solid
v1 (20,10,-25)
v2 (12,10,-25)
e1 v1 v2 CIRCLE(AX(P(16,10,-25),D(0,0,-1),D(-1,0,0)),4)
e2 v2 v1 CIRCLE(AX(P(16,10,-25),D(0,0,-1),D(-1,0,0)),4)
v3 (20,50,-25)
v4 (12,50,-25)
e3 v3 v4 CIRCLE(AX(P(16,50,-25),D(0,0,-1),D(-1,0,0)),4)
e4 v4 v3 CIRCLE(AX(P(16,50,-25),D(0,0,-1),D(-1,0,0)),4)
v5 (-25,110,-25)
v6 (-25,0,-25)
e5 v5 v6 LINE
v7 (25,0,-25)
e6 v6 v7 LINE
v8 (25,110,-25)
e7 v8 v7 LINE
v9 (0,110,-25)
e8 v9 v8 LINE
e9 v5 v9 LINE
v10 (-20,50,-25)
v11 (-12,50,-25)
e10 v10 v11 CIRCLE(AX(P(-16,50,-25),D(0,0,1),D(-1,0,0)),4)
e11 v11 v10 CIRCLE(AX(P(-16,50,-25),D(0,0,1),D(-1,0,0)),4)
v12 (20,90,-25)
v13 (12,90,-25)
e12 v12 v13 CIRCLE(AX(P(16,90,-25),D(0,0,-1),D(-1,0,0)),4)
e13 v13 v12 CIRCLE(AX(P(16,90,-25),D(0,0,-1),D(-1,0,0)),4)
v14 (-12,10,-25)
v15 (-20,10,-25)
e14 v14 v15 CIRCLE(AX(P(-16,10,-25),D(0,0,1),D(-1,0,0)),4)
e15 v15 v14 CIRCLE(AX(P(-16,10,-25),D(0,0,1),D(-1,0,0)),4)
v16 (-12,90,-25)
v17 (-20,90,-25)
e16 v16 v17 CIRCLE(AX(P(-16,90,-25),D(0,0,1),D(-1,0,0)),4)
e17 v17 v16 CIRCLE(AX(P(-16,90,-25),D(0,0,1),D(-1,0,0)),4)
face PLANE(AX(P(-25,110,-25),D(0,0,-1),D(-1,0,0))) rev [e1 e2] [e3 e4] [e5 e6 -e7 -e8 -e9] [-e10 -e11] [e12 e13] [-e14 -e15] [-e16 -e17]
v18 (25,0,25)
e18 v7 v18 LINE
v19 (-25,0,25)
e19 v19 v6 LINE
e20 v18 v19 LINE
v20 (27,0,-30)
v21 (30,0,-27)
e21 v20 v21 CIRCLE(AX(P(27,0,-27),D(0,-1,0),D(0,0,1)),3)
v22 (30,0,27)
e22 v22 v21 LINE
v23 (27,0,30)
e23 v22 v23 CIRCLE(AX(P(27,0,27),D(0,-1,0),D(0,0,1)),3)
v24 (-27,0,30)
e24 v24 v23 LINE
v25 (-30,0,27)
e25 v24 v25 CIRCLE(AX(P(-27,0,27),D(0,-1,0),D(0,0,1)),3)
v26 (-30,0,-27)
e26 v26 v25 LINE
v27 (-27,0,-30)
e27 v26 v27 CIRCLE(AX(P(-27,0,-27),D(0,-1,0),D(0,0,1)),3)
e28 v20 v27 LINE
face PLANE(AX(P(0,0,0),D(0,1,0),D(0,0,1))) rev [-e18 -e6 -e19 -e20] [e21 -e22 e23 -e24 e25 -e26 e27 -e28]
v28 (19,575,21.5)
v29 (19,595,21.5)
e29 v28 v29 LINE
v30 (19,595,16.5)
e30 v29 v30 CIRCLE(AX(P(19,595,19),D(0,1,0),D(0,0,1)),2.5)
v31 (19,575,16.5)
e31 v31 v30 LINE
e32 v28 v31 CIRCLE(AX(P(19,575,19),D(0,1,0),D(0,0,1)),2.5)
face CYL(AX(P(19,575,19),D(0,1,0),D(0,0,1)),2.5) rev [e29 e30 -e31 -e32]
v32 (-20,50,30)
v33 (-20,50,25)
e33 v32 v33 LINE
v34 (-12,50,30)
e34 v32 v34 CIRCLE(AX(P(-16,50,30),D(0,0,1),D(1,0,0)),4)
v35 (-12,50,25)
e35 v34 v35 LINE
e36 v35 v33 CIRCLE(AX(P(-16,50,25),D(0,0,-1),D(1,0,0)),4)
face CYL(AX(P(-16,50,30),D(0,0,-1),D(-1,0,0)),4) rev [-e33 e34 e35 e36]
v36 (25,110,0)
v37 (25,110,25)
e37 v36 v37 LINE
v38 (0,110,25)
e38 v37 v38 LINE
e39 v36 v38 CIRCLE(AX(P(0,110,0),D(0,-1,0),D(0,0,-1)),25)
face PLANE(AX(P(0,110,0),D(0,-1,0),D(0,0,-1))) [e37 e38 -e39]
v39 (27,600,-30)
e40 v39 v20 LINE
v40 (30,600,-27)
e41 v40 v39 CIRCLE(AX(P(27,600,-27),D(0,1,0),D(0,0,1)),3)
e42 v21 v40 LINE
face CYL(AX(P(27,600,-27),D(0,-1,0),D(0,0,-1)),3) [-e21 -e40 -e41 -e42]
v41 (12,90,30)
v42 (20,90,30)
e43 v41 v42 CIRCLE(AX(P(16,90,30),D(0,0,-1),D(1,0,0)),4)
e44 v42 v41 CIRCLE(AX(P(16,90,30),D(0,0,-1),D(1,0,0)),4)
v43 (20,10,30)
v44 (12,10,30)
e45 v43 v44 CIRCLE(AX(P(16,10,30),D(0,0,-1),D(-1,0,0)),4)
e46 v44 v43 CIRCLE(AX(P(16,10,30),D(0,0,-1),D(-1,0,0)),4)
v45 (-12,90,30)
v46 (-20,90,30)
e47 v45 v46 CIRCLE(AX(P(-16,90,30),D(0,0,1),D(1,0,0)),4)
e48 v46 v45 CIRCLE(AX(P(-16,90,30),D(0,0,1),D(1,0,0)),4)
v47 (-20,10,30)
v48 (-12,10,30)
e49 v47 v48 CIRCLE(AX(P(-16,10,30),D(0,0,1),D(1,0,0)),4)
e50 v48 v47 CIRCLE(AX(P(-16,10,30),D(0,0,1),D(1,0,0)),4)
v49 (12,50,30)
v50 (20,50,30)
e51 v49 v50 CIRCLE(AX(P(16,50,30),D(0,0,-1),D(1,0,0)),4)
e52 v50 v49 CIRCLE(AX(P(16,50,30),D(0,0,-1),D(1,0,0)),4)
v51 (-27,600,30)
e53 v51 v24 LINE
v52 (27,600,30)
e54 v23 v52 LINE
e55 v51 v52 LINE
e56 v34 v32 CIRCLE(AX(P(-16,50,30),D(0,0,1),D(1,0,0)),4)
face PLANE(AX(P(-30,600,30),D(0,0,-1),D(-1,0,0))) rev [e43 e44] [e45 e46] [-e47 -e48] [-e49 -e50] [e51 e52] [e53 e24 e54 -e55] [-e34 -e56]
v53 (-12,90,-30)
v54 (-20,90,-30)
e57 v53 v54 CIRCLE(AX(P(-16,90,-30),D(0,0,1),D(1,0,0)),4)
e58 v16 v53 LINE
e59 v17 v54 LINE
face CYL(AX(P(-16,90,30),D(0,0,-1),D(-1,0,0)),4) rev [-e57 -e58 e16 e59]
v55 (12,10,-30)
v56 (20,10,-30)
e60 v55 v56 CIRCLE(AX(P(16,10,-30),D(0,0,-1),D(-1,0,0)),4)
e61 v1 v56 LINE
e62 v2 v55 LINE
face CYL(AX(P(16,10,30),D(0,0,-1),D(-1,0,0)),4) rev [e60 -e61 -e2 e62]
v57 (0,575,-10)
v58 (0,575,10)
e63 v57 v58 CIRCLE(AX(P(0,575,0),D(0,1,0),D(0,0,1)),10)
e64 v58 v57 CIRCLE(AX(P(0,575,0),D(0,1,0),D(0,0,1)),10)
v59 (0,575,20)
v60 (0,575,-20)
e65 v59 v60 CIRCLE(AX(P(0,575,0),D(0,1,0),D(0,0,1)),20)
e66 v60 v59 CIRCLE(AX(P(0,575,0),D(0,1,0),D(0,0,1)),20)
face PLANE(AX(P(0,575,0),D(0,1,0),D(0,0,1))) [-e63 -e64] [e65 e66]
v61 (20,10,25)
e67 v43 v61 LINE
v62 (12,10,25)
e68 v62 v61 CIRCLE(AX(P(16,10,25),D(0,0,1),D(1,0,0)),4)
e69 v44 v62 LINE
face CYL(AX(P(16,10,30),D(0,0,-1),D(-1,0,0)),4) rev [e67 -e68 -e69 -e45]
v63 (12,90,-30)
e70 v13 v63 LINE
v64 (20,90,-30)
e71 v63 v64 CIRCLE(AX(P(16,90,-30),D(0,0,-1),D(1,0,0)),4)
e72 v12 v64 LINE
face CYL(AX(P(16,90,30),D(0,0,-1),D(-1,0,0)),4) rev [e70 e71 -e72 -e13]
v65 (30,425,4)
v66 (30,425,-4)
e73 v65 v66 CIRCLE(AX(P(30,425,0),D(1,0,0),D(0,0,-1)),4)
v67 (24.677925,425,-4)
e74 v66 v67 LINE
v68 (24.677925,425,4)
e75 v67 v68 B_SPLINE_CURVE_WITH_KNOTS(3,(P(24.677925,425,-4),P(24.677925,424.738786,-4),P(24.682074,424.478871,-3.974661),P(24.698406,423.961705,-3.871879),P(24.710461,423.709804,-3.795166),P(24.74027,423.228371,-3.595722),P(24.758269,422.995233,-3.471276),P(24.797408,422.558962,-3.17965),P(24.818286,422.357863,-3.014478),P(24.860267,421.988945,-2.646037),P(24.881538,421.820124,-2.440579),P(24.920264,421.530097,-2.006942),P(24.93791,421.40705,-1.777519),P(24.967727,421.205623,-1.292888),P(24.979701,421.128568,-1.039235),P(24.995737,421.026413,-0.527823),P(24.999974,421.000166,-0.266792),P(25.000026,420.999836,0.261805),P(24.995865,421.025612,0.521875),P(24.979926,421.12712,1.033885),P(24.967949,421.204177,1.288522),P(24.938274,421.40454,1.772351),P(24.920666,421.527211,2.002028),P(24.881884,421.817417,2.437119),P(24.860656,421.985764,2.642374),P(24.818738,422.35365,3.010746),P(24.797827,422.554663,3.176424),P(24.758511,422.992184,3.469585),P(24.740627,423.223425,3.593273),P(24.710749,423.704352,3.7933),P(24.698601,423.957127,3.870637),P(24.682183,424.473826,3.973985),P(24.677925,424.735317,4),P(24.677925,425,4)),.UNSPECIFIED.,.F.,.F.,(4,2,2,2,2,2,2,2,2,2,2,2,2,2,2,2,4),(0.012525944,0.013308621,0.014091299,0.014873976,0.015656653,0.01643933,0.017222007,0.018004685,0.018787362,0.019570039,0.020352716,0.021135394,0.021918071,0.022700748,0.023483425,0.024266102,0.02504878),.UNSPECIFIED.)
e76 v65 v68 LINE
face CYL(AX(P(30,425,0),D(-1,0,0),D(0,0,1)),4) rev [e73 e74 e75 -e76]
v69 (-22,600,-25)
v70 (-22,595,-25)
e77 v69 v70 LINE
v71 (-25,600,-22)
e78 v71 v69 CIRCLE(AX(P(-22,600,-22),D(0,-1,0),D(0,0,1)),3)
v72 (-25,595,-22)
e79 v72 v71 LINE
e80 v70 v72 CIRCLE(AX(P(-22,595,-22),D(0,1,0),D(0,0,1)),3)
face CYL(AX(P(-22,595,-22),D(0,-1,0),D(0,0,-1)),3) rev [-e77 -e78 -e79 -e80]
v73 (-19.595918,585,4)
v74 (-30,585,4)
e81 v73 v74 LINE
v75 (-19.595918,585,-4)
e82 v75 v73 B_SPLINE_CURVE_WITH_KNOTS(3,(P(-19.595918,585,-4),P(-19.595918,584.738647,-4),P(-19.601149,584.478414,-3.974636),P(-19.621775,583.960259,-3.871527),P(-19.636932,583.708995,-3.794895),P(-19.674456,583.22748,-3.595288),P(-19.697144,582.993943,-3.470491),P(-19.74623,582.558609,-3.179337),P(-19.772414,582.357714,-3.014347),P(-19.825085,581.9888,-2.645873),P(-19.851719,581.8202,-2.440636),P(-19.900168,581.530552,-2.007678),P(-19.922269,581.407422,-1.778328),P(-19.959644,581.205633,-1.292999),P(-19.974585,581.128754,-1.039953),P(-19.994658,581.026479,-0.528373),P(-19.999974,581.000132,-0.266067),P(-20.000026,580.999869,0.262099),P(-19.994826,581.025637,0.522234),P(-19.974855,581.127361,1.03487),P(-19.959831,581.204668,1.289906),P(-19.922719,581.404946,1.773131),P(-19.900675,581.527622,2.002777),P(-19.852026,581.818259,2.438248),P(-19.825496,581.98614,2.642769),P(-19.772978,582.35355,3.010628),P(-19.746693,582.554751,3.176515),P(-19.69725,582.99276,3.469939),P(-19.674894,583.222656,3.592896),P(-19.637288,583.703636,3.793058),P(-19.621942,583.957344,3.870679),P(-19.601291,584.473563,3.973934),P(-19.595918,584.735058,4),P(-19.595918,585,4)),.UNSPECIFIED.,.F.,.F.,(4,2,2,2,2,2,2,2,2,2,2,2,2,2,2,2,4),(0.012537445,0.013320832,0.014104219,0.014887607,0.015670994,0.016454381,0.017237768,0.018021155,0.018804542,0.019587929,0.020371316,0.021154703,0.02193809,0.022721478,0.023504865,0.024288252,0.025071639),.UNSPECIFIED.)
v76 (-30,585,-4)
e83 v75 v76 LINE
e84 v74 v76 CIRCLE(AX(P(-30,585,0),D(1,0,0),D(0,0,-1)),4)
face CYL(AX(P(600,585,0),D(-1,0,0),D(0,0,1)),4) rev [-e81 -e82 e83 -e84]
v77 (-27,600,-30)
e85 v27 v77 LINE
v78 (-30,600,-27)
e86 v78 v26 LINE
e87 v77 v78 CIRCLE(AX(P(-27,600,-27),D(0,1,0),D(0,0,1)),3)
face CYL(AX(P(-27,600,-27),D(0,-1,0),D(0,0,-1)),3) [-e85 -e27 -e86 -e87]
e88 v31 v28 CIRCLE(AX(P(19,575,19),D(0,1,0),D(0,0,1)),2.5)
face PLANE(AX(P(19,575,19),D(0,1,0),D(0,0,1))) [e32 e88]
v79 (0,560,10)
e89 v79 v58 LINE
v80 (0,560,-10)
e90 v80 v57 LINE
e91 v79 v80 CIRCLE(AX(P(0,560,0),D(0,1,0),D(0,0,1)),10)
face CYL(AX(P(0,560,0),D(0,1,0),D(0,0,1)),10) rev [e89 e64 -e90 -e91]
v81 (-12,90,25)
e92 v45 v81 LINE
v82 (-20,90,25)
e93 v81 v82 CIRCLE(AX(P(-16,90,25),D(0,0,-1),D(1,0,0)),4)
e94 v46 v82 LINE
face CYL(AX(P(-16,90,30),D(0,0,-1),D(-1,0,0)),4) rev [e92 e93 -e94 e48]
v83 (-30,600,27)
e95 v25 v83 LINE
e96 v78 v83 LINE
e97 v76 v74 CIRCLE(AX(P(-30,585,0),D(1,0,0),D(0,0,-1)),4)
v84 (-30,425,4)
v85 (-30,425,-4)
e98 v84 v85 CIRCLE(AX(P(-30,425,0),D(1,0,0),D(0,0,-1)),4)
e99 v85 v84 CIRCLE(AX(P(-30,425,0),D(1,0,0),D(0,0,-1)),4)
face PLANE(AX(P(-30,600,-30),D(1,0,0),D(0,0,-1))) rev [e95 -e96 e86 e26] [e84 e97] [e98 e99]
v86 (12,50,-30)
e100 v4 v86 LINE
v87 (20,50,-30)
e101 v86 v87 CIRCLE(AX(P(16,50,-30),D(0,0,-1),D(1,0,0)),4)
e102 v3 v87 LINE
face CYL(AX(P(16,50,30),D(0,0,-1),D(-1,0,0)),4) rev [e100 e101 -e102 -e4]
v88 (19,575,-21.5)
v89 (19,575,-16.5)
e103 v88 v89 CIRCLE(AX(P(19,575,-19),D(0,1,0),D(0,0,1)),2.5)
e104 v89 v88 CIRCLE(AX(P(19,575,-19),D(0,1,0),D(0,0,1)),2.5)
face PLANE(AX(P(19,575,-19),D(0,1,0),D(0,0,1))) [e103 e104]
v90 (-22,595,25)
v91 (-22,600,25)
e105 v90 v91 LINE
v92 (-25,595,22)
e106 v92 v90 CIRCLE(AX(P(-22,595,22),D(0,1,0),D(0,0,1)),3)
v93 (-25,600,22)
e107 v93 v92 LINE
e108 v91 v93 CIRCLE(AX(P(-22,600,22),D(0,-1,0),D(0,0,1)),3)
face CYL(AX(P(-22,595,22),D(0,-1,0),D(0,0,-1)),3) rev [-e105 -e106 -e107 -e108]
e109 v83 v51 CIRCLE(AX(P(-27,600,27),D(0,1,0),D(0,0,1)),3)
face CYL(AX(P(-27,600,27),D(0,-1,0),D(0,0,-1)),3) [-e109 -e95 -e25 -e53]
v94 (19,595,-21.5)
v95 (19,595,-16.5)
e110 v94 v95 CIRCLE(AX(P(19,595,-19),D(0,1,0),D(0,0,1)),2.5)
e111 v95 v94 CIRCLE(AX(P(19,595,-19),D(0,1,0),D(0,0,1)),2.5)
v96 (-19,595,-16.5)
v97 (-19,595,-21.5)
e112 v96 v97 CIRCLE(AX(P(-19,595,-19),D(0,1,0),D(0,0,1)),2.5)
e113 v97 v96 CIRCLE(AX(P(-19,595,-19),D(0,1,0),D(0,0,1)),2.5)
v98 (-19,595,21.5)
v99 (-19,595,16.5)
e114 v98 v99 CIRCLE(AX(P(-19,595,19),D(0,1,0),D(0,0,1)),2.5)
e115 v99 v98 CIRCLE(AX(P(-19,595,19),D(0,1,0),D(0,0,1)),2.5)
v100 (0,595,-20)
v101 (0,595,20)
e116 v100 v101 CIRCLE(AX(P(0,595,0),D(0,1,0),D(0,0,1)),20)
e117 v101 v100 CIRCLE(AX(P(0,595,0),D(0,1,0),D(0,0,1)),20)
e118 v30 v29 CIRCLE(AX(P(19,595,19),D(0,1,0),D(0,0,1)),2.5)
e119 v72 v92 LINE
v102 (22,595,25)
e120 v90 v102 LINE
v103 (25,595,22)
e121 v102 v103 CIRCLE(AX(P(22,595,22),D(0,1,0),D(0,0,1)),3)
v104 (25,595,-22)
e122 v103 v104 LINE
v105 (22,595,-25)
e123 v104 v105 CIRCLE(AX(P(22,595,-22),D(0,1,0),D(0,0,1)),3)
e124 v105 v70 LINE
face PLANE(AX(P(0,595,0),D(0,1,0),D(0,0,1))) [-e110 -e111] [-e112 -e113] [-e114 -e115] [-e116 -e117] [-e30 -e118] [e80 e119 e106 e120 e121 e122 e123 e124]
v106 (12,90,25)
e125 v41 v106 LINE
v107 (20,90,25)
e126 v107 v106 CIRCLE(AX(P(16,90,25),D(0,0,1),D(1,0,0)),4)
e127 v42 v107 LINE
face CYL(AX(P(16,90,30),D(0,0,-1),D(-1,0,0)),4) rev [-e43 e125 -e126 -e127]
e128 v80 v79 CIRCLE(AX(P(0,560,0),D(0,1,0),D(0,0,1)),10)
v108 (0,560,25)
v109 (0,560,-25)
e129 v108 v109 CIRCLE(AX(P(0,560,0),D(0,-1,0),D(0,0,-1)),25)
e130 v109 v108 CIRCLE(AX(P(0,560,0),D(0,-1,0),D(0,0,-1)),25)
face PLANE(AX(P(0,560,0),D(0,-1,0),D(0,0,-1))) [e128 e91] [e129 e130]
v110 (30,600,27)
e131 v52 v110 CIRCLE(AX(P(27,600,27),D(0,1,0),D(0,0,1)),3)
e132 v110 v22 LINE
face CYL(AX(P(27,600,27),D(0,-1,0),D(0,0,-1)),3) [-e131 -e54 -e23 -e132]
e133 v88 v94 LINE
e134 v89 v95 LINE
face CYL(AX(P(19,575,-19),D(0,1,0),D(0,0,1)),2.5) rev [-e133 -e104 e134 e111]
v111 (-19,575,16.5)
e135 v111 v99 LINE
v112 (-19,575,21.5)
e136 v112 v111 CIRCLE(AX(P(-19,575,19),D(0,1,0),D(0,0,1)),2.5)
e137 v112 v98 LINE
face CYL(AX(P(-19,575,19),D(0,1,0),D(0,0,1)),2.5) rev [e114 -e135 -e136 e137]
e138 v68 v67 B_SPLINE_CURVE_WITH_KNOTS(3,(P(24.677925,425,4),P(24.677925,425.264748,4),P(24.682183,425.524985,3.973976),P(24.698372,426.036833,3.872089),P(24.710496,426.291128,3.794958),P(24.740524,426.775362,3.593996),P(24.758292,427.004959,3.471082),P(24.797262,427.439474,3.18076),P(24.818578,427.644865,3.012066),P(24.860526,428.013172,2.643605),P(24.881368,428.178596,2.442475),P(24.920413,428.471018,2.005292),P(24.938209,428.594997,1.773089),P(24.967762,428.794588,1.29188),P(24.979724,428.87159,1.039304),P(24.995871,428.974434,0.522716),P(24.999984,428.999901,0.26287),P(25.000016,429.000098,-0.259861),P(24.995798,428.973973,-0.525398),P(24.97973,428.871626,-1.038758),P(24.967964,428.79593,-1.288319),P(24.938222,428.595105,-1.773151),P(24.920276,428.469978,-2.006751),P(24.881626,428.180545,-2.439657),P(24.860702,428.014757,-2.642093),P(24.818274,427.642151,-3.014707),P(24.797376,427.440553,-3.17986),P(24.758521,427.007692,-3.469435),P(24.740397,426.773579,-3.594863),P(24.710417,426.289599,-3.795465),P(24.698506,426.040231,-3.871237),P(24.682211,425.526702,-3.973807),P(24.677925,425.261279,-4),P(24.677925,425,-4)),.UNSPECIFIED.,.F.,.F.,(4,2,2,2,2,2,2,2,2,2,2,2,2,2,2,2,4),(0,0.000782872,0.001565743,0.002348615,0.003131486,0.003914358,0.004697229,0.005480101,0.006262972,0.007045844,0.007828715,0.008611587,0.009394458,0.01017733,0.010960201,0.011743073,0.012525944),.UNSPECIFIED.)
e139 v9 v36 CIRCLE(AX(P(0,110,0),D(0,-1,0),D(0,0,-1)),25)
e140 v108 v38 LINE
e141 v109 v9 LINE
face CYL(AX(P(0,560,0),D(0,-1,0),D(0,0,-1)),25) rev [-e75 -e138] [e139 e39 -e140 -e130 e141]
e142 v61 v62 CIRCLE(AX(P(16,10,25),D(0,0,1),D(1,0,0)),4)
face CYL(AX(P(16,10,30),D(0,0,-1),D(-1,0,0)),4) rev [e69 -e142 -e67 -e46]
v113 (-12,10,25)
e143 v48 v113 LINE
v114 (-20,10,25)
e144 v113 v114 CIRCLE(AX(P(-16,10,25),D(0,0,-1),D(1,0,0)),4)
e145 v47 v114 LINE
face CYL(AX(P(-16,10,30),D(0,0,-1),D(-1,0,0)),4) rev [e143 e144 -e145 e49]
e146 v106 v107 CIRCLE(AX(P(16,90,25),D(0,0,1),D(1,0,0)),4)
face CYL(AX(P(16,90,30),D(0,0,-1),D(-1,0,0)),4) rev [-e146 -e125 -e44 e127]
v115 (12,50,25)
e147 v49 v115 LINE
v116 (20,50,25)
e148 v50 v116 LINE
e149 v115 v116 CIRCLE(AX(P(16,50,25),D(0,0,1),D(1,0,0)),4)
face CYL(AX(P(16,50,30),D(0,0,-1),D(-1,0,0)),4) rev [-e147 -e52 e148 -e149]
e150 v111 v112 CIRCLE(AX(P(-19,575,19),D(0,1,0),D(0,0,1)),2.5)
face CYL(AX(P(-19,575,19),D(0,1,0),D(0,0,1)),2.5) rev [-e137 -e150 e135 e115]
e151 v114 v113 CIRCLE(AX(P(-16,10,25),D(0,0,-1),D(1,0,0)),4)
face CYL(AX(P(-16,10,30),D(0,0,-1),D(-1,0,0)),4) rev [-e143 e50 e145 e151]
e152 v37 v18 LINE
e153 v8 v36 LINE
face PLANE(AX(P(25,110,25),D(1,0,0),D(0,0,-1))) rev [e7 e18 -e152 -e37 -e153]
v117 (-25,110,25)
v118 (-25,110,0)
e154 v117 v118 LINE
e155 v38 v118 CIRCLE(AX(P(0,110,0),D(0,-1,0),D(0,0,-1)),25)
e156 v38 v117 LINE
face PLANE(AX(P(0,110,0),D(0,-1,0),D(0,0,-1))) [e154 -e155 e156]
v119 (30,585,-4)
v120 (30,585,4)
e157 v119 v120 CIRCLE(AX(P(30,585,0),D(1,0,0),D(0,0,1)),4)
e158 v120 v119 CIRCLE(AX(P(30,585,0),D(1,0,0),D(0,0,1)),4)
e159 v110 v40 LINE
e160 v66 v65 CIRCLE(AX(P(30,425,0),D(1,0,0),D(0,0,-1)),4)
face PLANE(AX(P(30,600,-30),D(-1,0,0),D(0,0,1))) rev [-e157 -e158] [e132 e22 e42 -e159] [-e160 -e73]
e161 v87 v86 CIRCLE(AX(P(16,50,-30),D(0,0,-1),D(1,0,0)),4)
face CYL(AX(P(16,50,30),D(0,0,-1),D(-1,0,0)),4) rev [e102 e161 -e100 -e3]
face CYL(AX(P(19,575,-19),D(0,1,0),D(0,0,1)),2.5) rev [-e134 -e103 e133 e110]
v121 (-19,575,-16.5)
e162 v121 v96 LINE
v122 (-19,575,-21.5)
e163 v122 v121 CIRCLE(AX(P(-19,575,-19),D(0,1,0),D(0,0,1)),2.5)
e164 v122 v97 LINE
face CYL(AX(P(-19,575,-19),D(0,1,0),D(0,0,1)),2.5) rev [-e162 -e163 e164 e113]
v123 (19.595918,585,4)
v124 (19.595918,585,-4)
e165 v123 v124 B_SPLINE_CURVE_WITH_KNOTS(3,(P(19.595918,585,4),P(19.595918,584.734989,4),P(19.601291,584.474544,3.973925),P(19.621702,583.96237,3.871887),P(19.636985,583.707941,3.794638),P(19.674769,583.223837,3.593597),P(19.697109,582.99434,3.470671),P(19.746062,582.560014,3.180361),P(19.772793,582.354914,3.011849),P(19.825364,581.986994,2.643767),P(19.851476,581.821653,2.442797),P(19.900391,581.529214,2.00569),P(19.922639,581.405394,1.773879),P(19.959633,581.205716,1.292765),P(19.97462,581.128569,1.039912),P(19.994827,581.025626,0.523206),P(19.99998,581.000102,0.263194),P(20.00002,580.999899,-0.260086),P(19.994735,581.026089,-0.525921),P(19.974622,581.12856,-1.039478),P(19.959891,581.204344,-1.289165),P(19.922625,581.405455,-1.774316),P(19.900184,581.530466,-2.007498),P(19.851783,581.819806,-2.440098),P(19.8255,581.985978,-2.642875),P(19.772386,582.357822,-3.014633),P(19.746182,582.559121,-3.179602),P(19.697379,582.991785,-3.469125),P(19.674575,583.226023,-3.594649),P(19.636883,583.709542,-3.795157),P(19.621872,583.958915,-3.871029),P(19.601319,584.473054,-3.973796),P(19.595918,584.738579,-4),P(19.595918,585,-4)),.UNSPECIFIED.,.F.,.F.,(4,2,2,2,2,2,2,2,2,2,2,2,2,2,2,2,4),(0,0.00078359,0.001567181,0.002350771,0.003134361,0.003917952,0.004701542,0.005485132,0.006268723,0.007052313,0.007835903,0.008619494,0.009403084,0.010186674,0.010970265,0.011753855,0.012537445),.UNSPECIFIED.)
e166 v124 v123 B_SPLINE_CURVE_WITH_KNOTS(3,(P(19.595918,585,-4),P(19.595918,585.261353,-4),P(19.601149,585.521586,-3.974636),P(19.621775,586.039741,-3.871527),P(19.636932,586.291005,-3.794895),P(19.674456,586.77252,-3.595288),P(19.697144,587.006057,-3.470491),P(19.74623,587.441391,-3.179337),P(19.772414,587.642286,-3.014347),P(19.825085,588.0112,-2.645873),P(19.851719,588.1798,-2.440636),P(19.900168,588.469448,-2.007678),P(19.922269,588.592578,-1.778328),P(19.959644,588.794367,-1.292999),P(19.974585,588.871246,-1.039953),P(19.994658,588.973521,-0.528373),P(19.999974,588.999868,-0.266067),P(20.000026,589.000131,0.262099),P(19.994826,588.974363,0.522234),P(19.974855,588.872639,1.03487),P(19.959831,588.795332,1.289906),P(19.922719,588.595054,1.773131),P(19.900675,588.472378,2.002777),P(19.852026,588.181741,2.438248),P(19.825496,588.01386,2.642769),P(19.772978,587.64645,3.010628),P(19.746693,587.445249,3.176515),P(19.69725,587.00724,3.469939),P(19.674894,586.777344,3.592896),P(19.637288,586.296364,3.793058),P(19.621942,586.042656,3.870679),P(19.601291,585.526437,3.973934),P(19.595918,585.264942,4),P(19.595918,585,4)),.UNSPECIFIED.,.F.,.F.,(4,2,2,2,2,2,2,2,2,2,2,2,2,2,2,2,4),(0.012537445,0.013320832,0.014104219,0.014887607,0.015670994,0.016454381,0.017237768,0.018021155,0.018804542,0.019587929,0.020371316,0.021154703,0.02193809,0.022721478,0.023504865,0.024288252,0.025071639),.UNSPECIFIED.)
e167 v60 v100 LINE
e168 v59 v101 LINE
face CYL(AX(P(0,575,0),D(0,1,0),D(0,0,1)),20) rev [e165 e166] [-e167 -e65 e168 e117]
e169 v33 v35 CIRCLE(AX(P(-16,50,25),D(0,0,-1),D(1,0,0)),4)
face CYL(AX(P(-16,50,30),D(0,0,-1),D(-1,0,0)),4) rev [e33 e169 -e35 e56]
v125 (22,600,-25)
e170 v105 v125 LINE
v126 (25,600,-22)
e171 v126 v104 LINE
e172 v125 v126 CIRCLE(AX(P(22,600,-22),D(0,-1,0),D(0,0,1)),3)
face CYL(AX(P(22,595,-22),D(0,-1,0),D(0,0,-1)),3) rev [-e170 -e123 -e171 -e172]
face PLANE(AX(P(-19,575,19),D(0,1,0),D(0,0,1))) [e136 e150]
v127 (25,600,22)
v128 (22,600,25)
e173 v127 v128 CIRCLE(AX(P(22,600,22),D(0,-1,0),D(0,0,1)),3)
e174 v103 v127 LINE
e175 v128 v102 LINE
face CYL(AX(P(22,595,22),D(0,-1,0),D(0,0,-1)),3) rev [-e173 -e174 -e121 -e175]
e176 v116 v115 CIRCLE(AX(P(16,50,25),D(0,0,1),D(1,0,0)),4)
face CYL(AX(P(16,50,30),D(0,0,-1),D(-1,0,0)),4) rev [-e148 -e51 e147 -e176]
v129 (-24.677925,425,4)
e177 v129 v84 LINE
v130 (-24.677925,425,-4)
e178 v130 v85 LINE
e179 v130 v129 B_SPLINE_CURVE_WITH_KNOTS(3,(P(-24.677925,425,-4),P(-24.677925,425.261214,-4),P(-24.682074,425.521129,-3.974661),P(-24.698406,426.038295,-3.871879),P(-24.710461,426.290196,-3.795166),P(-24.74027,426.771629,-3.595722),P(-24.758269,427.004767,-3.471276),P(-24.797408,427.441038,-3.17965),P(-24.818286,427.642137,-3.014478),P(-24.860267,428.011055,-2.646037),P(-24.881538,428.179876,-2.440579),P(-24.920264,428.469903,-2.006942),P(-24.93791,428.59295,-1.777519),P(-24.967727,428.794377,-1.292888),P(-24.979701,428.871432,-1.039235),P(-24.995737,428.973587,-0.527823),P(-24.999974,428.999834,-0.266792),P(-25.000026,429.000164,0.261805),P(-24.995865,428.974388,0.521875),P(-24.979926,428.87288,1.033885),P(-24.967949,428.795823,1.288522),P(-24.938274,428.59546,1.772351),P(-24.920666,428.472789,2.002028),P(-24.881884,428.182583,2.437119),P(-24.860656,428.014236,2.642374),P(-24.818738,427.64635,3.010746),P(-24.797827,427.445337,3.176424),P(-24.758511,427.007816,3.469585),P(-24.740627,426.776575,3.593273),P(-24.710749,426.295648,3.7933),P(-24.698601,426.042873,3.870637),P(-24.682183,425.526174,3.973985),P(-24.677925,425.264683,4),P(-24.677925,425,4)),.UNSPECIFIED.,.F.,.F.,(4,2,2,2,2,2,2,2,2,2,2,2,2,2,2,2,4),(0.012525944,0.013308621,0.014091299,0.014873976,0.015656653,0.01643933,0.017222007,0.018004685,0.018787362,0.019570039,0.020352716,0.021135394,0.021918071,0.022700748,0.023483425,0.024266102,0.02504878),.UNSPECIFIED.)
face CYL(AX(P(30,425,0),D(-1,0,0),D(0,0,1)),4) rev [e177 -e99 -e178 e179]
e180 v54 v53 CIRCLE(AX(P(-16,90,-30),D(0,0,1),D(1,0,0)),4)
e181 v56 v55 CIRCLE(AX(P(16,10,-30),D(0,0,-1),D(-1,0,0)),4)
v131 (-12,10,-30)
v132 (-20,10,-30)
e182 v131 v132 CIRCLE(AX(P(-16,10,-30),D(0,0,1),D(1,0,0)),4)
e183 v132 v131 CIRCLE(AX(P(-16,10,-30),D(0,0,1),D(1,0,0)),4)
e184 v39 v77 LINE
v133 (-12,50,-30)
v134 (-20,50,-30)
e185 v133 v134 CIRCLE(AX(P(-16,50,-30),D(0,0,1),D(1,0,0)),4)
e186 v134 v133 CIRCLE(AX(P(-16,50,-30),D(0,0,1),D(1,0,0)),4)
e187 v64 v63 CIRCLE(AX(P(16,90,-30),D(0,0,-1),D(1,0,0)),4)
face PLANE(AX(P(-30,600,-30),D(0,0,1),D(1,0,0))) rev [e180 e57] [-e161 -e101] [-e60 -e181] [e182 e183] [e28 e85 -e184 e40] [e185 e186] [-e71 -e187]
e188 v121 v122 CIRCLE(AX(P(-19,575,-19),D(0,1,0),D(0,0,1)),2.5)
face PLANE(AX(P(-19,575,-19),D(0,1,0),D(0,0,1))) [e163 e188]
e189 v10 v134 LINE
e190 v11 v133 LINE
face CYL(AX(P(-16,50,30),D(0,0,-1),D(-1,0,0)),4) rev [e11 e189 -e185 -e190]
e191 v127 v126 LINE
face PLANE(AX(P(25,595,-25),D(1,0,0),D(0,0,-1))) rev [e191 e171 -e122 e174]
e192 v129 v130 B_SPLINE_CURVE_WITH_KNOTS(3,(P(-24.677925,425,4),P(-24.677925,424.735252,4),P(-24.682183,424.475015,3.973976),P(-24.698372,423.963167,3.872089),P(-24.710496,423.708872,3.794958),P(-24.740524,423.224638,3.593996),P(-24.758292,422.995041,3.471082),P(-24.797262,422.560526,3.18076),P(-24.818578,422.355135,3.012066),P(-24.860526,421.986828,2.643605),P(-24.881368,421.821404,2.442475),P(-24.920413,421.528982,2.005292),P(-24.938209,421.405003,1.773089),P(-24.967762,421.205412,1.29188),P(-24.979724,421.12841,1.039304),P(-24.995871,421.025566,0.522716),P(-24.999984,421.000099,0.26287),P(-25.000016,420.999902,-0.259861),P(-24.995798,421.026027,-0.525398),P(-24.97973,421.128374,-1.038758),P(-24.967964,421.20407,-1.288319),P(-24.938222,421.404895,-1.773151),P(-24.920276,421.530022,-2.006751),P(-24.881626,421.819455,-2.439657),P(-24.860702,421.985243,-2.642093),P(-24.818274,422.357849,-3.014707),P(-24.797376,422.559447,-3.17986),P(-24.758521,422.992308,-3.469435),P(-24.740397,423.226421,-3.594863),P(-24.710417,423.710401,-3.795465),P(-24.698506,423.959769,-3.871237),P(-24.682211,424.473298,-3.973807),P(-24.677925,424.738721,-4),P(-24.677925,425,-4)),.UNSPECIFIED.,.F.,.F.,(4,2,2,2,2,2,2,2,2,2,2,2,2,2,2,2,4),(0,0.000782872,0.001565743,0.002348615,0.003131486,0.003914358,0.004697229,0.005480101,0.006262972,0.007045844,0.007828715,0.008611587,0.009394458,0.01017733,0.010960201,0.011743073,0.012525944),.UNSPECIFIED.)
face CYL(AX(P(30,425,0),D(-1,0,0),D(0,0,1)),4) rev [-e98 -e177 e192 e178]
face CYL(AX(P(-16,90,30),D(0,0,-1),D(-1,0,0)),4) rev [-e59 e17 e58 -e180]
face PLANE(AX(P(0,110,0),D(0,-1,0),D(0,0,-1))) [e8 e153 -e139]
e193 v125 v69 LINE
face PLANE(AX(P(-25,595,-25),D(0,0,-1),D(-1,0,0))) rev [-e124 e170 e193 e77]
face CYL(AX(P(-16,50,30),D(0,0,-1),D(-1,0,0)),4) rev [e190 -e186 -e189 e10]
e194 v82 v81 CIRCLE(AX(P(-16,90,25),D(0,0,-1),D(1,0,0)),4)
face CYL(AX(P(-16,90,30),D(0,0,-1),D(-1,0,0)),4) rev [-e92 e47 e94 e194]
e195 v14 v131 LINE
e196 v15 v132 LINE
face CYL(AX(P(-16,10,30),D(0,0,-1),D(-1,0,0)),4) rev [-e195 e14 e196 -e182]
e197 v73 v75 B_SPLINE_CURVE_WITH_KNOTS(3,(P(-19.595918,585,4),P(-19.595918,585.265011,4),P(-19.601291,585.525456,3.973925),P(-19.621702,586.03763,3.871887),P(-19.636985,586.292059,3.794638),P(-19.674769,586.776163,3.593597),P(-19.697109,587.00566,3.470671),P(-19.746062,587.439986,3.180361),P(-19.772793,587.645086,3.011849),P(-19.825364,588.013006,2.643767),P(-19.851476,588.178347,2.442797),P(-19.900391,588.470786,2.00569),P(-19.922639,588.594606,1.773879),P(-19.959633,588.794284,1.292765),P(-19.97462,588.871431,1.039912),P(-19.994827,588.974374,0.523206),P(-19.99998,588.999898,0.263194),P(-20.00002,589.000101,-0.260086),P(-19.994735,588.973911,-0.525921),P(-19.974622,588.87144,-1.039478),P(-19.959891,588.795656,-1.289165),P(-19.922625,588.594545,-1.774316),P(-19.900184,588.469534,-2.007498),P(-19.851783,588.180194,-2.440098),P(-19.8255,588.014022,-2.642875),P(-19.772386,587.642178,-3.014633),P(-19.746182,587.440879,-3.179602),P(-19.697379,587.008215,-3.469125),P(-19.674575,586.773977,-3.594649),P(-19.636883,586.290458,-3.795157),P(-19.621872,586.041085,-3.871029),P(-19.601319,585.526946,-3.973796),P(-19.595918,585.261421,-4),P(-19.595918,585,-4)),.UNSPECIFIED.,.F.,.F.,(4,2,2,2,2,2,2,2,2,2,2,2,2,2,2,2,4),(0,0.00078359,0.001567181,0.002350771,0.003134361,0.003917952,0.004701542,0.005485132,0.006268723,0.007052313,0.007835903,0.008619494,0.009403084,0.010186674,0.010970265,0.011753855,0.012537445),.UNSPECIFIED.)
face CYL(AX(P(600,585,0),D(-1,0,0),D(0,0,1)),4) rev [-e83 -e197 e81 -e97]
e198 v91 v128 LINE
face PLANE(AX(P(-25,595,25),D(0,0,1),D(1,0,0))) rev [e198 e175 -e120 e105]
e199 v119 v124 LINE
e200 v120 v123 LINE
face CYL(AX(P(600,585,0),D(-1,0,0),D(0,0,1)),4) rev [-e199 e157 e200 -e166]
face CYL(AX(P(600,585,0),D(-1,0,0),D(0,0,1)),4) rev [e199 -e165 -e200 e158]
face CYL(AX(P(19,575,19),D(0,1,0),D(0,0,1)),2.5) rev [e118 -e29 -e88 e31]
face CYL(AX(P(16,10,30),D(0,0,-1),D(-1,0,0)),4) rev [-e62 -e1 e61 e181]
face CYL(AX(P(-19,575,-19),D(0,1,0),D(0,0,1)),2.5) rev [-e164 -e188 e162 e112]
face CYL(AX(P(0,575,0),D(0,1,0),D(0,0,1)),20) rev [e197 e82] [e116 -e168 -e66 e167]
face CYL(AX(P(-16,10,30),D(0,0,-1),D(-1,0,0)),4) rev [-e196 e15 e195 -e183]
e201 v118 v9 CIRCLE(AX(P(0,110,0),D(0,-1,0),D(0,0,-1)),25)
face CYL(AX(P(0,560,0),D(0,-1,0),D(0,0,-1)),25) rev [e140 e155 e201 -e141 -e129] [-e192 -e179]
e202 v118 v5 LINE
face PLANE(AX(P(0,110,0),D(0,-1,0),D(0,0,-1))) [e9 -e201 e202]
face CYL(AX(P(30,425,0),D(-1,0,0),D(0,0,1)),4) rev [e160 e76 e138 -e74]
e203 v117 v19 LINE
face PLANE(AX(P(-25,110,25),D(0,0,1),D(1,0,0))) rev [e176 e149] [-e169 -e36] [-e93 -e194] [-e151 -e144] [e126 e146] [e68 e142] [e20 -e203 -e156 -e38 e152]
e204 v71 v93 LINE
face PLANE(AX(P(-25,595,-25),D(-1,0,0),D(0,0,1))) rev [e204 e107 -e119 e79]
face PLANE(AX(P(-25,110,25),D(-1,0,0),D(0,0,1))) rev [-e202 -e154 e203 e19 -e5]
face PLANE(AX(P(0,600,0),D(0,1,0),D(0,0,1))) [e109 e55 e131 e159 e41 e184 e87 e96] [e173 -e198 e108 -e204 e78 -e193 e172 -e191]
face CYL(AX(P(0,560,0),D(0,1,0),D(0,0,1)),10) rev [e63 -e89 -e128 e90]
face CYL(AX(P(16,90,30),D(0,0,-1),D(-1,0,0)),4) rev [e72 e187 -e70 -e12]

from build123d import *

# Parameters (mm, degrees)
SKETCH1_W               = 60
SKETCH1_H               = 60
BOSS_EXTRUDE1_DEPTH     = 600
SKETCH2_W               = 50
SKETCH2_H               = 50
CUT_EXTRUDE1_DEPTH      = 5
CUT_EXTRUDE3_DEPTH      = 600
CUT_EXTRUDE3_DEPTH_BACK = 30
SKETCH4_R               = 4
FILLET2_R               = 3
SKETCH3_R               = 20
CUT_EXTRUDE4_DEPTH      = 20
SKETCH5_W               = 50
SKETCH5_H               = 50
CUT_EXTRUDE5_DEPTH      = 110
SKETCH6_R               = 25
CUT_EXTRUDE6_DEPTH      = 450
SKETCH7_R               = 10
CUT_EXTRUDE7_DEPTH      = 15
FILLET4_R               = 3
CUT_EXTRUDE8_DEPTH      = 30
CUT_EXTRUDE8_DEPTH_BACK = 30
SKETCH8_R               = 4
CUT_EXTRUDE9_DEPTH      = 30
CUT_EXTRUDE9_DEPTH_BACK = 30
SKETCH9_R               = 4
SKETCH10_R              = 2.5
CUT_EXTRUDE10_DEPTH     = 20


with BuildPart() as part:
    # Sketch1 → Boss-Extrude1 (new body)
    with BuildSketch(Plane(origin=(0, 0, 0), x_dir=(1, 0, 0), z_dir=(0, 1, 0))):
        Rectangle(SKETCH1_W, SKETCH1_H)
    extrude(amount=BOSS_EXTRUDE1_DEPTH)

    # Sketch2 → Cut-Extrude1 (cut)
    with BuildSketch(Plane(origin=(0, 600, 0), x_dir=(1, 0, 0), z_dir=(0, 1, 0))):
        Rectangle(SKETCH2_W, SKETCH2_H)
    extrude(amount=-CUT_EXTRUDE1_DEPTH, mode=Mode.SUBTRACT)

    # Sketch4 → Cut-Extrude3 (cut, two sides: drawn at the far end of the back side and taken through both)
    with BuildSketch(Plane(origin=(0, 0, 0), x_dir=(0, 0, -1), z_dir=(1, 0, 0)).offset(-CUT_EXTRUDE3_DEPTH_BACK)):
        with Locations(Location((0, 585, 0), (0, 0, 180))):
            Circle(SKETCH4_R)
    extrude(amount=CUT_EXTRUDE3_DEPTH + CUT_EXTRUDE3_DEPTH_BACK, mode=Mode.SUBTRACT)

    # Fillet2
    fillet2_edges = [part.edges().sort_by_distance(p)[0] for p in [
        (30, 300, 30),
        (-30, 300, 30),
        (-30, 300, -30),
        (30, 300, -30),
    ]]
    fillet(fillet2_edges, radius=FILLET2_R)

    # Sketch3 → Cut-Extrude4 (cut)
    with BuildSketch(Plane(origin=(0, 595, 0), x_dir=(1, 0, 0), z_dir=(0, 1, 0))):
        with Locations(Location((0, 0, 0), (0, 0, 270))):
            Circle(SKETCH3_R)
    extrude(amount=-CUT_EXTRUDE4_DEPTH, mode=Mode.SUBTRACT)

    # Sketch5 → Cut-Extrude5 (cut)
    with BuildSketch(Plane.XZ):
        Rectangle(SKETCH5_W, SKETCH5_H)
    extrude(amount=-CUT_EXTRUDE5_DEPTH, mode=Mode.SUBTRACT)

    # Sketch6 → Cut-Extrude6 (cut)
    with BuildSketch(Plane.XZ.offset(-110)):
        with Locations(Location((0, 0, 0), (0, 0, 270))):
            Circle(SKETCH6_R)
    extrude(amount=-CUT_EXTRUDE6_DEPTH, mode=Mode.SUBTRACT)

    # Sketch7 → Cut-Extrude7 (cut)
    with BuildSketch(Plane(origin=(0, 575, 0), x_dir=(1, 0, 0), z_dir=(0, 1, 0))):
        with Locations(Location((0, 0, 0), (0, 0, 270))):
            Circle(SKETCH7_R)
    extrude(amount=-CUT_EXTRUDE7_DEPTH, mode=Mode.SUBTRACT)

    # Fillet4
    fillet4_edges = [part.edges().sort_by_distance(p)[0] for p in [
        (25, 597.5, -25),
        (25, 597.5, 25),
        (-25, 597.5, 25),
        (-25, 597.5, -25),
    ]]
    fillet(fillet4_edges, radius=FILLET4_R)

    # Sketch8 → Cut-Extrude8 (cut, two sides: drawn at the far end of the back side and taken through both)
    with BuildSketch(Plane(origin=(0, 0, 0), x_dir=(0, 0, -1), z_dir=(1, 0, 0)).offset(-CUT_EXTRUDE8_DEPTH_BACK)):
        with Locations(Location((0, 425, 0), (0, 0, 180))):
            Circle(SKETCH8_R)
    extrude(amount=CUT_EXTRUDE8_DEPTH + CUT_EXTRUDE8_DEPTH_BACK, mode=Mode.SUBTRACT)

    # Sketch9 → Cut-Extrude9 (cut, two sides: drawn at the far end of the back side and taken through both)
    with BuildSketch(Plane.XY.offset(-CUT_EXTRUDE9_DEPTH_BACK)):
        with Locations((-16, 50)):
            Circle(SKETCH9_R)
        with Locations((16, 90)):
            Circle(SKETCH9_R)
        with Locations((16, 50)):
            Circle(SKETCH9_R)
        with Locations((-16, 90)):
            Circle(SKETCH9_R)
        with Locations(Location((16, 10, 0), (0, 0, 180))):
            Circle(SKETCH9_R)
        with Locations((-16, 10)):
            Circle(SKETCH9_R)
    extrude(amount=CUT_EXTRUDE9_DEPTH + CUT_EXTRUDE9_DEPTH_BACK, mode=Mode.SUBTRACT)

    # Sketch10 → Cut-Extrude10 (cut)
    with BuildSketch(Plane(origin=(0, 595, 0), x_dir=(1, 0, 0), z_dir=(0, 1, 0))):
        with Locations(Location((-19, 19, 0), (0, 0, 270))):
            Circle(SKETCH10_R)
        with Locations(Location((19, 19, 0), (0, 0, 270))):
            Circle(SKETCH10_R)
        with Locations(Location((19, -19, 0), (0, 0, 270))):
            Circle(SKETCH10_R)
        with Locations(Location((-19, -19, 0), (0, 0, 270))):
            Circle(SKETCH10_R)
    extrude(amount=-CUT_EXTRUDE10_DEPTH, mode=Mode.SUBTRACT)


solid = part.part
